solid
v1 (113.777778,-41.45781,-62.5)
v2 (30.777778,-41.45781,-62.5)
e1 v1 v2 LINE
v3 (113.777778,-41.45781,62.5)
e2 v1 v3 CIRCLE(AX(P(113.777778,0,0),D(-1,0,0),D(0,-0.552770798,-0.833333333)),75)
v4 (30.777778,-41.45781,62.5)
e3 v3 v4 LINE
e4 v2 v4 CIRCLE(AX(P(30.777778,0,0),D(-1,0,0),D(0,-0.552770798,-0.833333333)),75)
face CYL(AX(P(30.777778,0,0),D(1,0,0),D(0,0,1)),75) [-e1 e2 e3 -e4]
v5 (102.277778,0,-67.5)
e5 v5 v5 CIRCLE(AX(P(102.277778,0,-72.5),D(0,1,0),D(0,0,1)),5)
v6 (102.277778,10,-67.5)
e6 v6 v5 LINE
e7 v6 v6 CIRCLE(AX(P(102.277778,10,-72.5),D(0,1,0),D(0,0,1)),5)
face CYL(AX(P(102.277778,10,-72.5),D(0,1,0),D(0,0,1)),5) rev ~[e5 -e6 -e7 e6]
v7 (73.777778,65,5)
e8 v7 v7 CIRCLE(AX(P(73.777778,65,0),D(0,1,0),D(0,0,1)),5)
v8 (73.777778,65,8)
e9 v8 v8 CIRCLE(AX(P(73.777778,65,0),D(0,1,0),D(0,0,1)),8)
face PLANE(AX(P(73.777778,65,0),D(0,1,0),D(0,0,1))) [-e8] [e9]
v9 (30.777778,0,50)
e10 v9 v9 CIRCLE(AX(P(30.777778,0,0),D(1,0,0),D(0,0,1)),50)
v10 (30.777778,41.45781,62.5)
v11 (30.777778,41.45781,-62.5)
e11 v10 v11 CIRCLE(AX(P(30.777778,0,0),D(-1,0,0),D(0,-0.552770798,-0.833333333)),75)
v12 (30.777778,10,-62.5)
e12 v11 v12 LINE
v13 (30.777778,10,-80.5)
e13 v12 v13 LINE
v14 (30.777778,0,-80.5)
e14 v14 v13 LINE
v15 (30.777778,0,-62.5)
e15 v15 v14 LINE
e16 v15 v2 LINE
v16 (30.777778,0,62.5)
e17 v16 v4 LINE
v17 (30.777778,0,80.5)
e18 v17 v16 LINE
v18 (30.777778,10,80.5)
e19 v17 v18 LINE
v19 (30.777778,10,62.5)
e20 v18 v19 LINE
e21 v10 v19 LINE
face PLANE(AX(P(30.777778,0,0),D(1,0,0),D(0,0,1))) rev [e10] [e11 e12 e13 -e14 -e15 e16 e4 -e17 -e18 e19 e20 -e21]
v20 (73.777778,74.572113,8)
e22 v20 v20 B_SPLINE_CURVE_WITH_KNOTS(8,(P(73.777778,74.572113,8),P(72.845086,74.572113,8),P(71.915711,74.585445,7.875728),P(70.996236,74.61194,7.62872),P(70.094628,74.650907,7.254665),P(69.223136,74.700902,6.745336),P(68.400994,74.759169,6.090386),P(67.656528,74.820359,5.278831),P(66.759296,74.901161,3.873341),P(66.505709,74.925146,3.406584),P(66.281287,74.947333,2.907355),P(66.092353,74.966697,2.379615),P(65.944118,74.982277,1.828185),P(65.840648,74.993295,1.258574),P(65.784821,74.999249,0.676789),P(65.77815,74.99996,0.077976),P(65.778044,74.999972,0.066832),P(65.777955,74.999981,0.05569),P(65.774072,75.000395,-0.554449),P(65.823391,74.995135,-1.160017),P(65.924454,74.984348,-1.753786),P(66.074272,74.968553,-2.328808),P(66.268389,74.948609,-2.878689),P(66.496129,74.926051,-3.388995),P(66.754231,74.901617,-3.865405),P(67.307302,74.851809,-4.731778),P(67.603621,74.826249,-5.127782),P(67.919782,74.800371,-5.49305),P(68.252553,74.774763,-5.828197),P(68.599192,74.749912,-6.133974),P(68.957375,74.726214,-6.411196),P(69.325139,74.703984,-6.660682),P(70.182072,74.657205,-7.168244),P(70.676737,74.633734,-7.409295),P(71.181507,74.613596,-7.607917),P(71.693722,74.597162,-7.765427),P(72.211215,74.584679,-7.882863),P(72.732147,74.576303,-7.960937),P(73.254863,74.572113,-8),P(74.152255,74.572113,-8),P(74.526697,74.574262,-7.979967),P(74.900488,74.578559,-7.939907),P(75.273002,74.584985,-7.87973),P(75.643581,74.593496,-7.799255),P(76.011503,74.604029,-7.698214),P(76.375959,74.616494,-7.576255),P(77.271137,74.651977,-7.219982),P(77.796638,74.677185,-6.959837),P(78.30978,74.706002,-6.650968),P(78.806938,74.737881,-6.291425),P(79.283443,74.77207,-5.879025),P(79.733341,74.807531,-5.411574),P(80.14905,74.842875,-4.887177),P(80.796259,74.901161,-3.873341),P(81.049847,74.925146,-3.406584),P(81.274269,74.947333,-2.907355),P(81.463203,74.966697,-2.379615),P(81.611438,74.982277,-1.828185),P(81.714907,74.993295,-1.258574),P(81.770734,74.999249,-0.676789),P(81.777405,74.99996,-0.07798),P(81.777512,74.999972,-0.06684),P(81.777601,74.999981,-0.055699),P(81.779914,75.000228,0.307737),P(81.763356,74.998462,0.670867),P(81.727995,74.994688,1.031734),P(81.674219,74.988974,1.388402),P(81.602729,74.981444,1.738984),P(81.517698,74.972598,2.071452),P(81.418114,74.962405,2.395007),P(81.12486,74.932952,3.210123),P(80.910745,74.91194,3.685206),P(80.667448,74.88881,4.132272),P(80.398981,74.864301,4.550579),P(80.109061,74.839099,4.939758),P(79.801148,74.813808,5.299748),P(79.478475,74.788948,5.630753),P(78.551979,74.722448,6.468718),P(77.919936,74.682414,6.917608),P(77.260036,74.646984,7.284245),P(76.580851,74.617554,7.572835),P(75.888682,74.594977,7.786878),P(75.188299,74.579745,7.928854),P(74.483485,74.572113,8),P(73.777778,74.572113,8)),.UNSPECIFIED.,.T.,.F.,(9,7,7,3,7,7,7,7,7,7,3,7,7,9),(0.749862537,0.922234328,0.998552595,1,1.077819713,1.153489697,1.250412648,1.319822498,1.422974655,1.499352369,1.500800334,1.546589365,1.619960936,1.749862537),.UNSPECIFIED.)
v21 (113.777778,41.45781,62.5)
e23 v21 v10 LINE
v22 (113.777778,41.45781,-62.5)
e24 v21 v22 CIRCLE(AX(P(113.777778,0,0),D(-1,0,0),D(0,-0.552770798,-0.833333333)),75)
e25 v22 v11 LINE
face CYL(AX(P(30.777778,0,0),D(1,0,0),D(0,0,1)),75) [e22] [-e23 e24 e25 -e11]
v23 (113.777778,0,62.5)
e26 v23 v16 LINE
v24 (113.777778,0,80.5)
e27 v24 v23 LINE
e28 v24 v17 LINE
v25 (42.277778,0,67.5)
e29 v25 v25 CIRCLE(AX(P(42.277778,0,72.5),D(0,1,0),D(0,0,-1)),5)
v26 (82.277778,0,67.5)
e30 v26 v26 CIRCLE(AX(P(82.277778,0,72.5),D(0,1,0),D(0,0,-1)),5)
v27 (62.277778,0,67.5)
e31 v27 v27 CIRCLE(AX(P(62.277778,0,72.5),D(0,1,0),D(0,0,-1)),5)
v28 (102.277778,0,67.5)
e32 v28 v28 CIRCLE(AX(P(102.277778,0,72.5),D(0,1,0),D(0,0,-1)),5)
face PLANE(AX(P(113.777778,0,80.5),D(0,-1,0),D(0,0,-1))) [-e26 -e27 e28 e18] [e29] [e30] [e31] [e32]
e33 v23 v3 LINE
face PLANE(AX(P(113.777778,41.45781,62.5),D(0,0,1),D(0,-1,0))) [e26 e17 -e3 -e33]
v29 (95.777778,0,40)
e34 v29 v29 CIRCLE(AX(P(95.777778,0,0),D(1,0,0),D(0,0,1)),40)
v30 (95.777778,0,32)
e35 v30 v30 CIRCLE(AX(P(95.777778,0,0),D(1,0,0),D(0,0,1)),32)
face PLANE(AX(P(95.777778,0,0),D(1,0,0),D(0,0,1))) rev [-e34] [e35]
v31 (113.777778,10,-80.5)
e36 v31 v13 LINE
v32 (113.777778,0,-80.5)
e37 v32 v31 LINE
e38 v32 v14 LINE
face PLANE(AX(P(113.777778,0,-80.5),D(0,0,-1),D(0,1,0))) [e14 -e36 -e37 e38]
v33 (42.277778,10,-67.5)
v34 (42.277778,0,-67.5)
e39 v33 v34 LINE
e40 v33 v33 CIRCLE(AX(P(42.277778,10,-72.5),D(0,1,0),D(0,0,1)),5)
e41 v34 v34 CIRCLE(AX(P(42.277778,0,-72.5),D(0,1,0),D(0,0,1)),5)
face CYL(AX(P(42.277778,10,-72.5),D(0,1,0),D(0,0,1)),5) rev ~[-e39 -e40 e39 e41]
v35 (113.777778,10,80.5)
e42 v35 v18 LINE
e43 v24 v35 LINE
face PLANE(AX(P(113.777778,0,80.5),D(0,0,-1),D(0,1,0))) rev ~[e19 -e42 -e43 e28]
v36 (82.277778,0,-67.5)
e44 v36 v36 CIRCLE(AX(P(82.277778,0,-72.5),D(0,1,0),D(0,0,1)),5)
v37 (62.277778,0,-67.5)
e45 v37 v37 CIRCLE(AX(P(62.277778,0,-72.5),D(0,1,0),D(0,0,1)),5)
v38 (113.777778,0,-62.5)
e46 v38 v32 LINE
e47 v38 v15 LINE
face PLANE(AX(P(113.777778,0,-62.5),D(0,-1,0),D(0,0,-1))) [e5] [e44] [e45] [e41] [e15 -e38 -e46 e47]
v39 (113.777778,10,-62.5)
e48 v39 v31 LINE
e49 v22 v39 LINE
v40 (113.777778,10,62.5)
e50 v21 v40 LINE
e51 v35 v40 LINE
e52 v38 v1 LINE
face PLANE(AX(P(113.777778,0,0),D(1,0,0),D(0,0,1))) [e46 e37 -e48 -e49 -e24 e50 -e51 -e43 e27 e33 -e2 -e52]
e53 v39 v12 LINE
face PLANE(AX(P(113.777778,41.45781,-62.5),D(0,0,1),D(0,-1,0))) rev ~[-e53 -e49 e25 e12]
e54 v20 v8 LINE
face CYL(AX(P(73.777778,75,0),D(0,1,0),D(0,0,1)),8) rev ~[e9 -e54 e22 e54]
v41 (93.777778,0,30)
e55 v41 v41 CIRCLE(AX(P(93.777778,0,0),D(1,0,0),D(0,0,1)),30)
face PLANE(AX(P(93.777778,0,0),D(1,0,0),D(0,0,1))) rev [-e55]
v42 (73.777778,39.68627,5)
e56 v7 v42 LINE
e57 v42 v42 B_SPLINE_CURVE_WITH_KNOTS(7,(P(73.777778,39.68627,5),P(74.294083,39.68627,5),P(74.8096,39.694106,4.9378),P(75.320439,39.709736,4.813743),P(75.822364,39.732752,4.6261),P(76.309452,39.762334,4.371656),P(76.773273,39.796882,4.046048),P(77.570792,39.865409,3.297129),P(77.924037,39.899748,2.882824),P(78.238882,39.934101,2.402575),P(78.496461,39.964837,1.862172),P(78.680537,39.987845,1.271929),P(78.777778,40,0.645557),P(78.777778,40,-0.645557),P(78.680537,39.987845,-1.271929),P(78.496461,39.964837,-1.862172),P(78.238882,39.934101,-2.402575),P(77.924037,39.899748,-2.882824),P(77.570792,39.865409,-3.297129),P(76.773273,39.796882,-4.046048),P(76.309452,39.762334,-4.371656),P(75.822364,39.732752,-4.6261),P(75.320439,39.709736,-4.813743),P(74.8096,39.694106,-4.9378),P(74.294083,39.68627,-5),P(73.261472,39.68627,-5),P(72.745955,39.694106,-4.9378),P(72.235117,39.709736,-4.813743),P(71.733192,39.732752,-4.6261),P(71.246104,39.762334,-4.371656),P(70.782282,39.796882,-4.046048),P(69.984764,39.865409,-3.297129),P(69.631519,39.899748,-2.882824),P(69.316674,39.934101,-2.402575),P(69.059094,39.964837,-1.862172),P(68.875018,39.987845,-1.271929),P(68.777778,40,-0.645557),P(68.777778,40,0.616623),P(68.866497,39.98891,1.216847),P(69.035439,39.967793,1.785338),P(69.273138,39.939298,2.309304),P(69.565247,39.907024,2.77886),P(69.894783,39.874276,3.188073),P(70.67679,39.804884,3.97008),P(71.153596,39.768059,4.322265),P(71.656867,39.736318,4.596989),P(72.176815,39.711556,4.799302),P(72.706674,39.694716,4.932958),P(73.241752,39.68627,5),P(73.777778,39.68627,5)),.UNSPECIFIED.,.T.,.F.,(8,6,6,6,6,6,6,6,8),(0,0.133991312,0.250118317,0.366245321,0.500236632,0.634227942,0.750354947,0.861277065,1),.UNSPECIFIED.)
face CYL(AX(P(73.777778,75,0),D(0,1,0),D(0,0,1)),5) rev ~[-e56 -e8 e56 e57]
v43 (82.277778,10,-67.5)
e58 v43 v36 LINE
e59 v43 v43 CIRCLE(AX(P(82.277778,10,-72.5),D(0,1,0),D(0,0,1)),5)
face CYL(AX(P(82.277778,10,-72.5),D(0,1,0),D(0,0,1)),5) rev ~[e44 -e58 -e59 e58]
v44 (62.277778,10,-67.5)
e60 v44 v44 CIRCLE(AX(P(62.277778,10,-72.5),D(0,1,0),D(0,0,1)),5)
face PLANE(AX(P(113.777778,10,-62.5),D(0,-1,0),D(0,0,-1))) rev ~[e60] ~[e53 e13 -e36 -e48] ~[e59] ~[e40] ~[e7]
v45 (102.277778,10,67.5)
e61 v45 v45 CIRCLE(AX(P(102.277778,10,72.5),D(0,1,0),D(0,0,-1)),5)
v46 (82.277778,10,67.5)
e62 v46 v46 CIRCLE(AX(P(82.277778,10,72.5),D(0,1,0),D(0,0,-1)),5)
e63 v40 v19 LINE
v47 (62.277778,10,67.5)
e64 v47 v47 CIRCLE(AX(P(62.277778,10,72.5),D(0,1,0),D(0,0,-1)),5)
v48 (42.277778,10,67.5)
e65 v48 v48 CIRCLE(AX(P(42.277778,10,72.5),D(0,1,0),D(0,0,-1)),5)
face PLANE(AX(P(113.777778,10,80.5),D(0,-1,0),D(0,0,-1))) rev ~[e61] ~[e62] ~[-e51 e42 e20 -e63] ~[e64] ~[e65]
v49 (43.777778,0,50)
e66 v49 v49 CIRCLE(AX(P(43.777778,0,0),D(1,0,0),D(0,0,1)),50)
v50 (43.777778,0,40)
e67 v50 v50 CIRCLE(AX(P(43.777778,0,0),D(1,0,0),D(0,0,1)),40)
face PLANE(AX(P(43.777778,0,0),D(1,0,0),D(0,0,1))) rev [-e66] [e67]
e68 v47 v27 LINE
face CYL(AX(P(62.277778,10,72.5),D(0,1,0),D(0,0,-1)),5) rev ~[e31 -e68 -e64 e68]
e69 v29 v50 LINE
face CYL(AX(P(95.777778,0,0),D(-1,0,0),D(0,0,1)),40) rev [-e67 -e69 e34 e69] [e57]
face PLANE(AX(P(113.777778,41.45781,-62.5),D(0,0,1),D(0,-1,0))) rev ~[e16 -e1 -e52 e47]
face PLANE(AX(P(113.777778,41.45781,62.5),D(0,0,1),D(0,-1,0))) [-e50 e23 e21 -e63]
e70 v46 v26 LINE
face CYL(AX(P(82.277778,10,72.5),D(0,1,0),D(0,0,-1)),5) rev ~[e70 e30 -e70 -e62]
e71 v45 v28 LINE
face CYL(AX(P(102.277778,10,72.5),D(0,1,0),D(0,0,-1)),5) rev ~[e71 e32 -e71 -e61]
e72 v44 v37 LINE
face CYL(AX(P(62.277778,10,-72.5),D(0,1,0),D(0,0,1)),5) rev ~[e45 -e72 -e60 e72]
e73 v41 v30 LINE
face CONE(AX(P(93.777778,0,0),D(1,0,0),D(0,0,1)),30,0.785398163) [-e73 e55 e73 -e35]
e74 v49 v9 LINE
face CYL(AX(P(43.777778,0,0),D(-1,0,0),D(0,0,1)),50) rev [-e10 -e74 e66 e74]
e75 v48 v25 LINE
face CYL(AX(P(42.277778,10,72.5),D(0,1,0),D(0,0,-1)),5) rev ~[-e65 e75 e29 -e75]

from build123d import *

# Parameters (mm, degrees)
CUT_EXTRUDE_1_REACH      = 136.681
SKETCH_9_W               = 18
SKETCH_9_H               = 10
EXTRUDE_1_DEPTH          = 83
CUT_EXTRUDE_4_REACH      = 165.25
SKETCH_10_R              = 5
CUT_EXTRUDE_5_REACH      = 206.757
CUT_EXTRUDE_5_END_RADIUS = 40
SKETCH_11_R              = 5
SKETCH_12_R              = 8
CUT_EXTRUDE_6_DEPTH      = 10


with BuildPart() as part:
    # 草图1 → 旋转1 (revolve)
    with BuildSketch(Plane.XY, mode=Mode.PRIVATE) as revolve_1_sk:
        Polygon((30.777777778, 50), (30.777777778, 75), (113.777777778, 75), (113.777777778, 0), (93.777777778, 0), (93.777777778, 30), (95.777777778, 32), (95.777777778, 40), (43.777777778, 40), (43.777777778, 50), align=None)
    revolve(revolve_1_sk.sketch.rotate(Axis((-130.37037037, 0, 0), (1, 0, 0)), 90), axis=Axis((-130.37037037, 0, 0), (1, 0, 0)))

    # 草图6 → 切除-拉伸1 (cut, up to next)
    with BuildSketch(Plane(origin=(113.777777778, 0, 0), x_dir=(0, 0, -1), z_dir=(1, 0, 0)), mode=Mode.PRIVATE) as cut_extrude_1_sk1:
        with BuildLine():
            Line((62.5, 41.457809879), (62.5, -41.457809879))
            ThreePointArc((62.5, -41.457809879), (75, 0), (62.5, 41.457809879))
        make_face()
    cut_extrude_1_tool1 = extrude(cut_extrude_1_sk1.sketch, amount=-CUT_EXTRUDE_1_REACH, mode=Mode.PRIVATE) & part.part
    # 草图6 → 切除-拉伸1 (cut, up to next)
    with BuildSketch(Plane(origin=(113.777777778, 0, 0), x_dir=(0, 0, -1), z_dir=(1, 0, 0)), mode=Mode.PRIVATE) as cut_extrude_1_sk2:
        with BuildLine():
            Line((-62.5, 41.457809879), (-62.5, -41.457809879))
            ThreePointArc((-62.5, -41.457809879), (-75, 0), (-62.5, 41.457809879))
        make_face()
    cut_extrude_1_tool2 = extrude(cut_extrude_1_sk2.sketch, amount=-CUT_EXTRUDE_1_REACH, mode=Mode.PRIVATE) & part.part
    add(cut_extrude_1_tool1.solids().sort_by_distance((113.777778, 0, -67.537528))[0], mode=Mode.SUBTRACT)
    add(cut_extrude_1_tool2.solids().sort_by_distance((113.777778, 0, 67.537528))[0], mode=Mode.SUBTRACT)

    # 草图9 → 凸台-拉伸1 (add)
    with BuildSketch(Plane(origin=(113.777777778, 0, 0), x_dir=(0, 0, -1), z_dir=(1, 0, 0))):
        with Locations((-71.5, 5)):
            Rectangle(SKETCH_9_W, SKETCH_9_H)
        with Locations((71.5, 5)):
            Rectangle(SKETCH_9_W, SKETCH_9_H)
    extrude(amount=-EXTRUDE_1_DEPTH)

    # 草图10 → 切除-拉伸4 (cut, up to next)
    with BuildSketch(Plane(origin=(0, 10, 0), x_dir=(1, 0, 0), z_dir=(0, 1, 0)), mode=Mode.PRIVATE) as cut_extrude_4_sk1:
        with Locations(Location((42.277777778, 72.5, 0), (0, 0, 270))):
            Circle(SKETCH_10_R)
    cut_extrude_4_tool1 = extrude(cut_extrude_4_sk1.sketch, amount=-CUT_EXTRUDE_4_REACH, mode=Mode.PRIVATE) & part.part
    # 草图10 → 切除-拉伸4 (cut, up to next)
    with BuildSketch(Plane(origin=(0, 10, 0), x_dir=(1, 0, 0), z_dir=(0, 1, 0)), mode=Mode.PRIVATE) as cut_extrude_4_sk2:
        with Locations(Location((62.277777778, 72.5, 0), (0, 0, 270))):
            Circle(SKETCH_10_R)
    cut_extrude_4_tool2 = extrude(cut_extrude_4_sk2.sketch, amount=-CUT_EXTRUDE_4_REACH, mode=Mode.PRIVATE) & part.part
    # 草图10 → 切除-拉伸4 (cut, up to next)
    with BuildSketch(Plane(origin=(0, 10, 0), x_dir=(1, 0, 0), z_dir=(0, 1, 0)), mode=Mode.PRIVATE) as cut_extrude_4_sk3:
        with Locations(Location((82.277777778, 72.5, 0), (0, 0, 270))):
            Circle(SKETCH_10_R)
    cut_extrude_4_tool3 = extrude(cut_extrude_4_sk3.sketch, amount=-CUT_EXTRUDE_4_REACH, mode=Mode.PRIVATE) & part.part
    # 草图10 → 切除-拉伸4 (cut, up to next)
    with BuildSketch(Plane(origin=(0, 10, 0), x_dir=(1, 0, 0), z_dir=(0, 1, 0)), mode=Mode.PRIVATE) as cut_extrude_4_sk4:
        with Locations(Location((102.277777778, 72.5, 0), (0, 0, 270))):
            Circle(SKETCH_10_R)
    cut_extrude_4_tool4 = extrude(cut_extrude_4_sk4.sketch, amount=-CUT_EXTRUDE_4_REACH, mode=Mode.PRIVATE) & part.part
    # 草图10 → 切除-拉伸4 (cut, up to next)
    with BuildSketch(Plane(origin=(0, 10, 0), x_dir=(1, 0, 0), z_dir=(0, 1, 0)), mode=Mode.PRIVATE) as cut_extrude_4_sk5:
        with Locations(Location((102.277777778, -72.5, 0), (0, 0, 90))):
            Circle(SKETCH_10_R)
    cut_extrude_4_tool5 = extrude(cut_extrude_4_sk5.sketch, amount=-CUT_EXTRUDE_4_REACH, mode=Mode.PRIVATE) & part.part
    # 草图10 → 切除-拉伸4 (cut, up to next)
    with BuildSketch(Plane(origin=(0, 10, 0), x_dir=(1, 0, 0), z_dir=(0, 1, 0)), mode=Mode.PRIVATE) as cut_extrude_4_sk6:
        with Locations(Location((82.277777778, -72.5, 0), (0, 0, 90))):
            Circle(SKETCH_10_R)
    cut_extrude_4_tool6 = extrude(cut_extrude_4_sk6.sketch, amount=-CUT_EXTRUDE_4_REACH, mode=Mode.PRIVATE) & part.part
    # 草图10 → 切除-拉伸4 (cut, up to next)
    with BuildSketch(Plane(origin=(0, 10, 0), x_dir=(1, 0, 0), z_dir=(0, 1, 0)), mode=Mode.PRIVATE) as cut_extrude_4_sk7:
        with Locations(Location((62.277777778, -72.5, 0), (0, 0, 90))):
            Circle(SKETCH_10_R)
    cut_extrude_4_tool7 = extrude(cut_extrude_4_sk7.sketch, amount=-CUT_EXTRUDE_4_REACH, mode=Mode.PRIVATE) & part.part
    # 草图10 → 切除-拉伸4 (cut, up to next)
    with BuildSketch(Plane(origin=(0, 10, 0), x_dir=(1, 0, 0), z_dir=(0, 1, 0)), mode=Mode.PRIVATE) as cut_extrude_4_sk8:
        with Locations(Location((42.277777778, -72.5, 0), (0, 0, 90))):
            Circle(SKETCH_10_R)
    cut_extrude_4_tool8 = extrude(cut_extrude_4_sk8.sketch, amount=-CUT_EXTRUDE_4_REACH, mode=Mode.PRIVATE) & part.part
    add(cut_extrude_4_tool1.solids().sort_by_distance((42.277778, 10, -72.5))[0], mode=Mode.SUBTRACT)
    add(cut_extrude_4_tool2.solids().sort_by_distance((62.277778, 10, -72.5))[0], mode=Mode.SUBTRACT)
    add(cut_extrude_4_tool3.solids().sort_by_distance((82.277778, 10, -72.5))[0], mode=Mode.SUBTRACT)
    add(cut_extrude_4_tool4.solids().sort_by_distance((102.277778, 10, -72.5))[0], mode=Mode.SUBTRACT)
    add(cut_extrude_4_tool5.solids().sort_by_distance((102.277778, 10, 72.5))[0], mode=Mode.SUBTRACT)
    add(cut_extrude_4_tool6.solids().sort_by_distance((82.277778, 10, 72.5))[0], mode=Mode.SUBTRACT)
    add(cut_extrude_4_tool7.solids().sort_by_distance((62.277778, 10, 72.5))[0], mode=Mode.SUBTRACT)
    add(cut_extrude_4_tool8.solids().sort_by_distance((42.277778, 10, 72.5))[0], mode=Mode.SUBTRACT)

    # 切除-拉伸5: up to this cylinder (the profile starts outside it)
    cut_extrude_5_end = Plane(origin=(73.777778, 0, 0), z_dir=(-1, 0, 0)) * Cylinder(CUT_EXTRUDE_5_END_RADIUS, 494.514, mode=Mode.PRIVATE)
    # 草图11 → 切除-拉伸5 (cut, up to the surface)
    with BuildSketch(Plane(origin=(0, 75, 0), x_dir=(1, 0, 0), z_dir=(0, 1, 0)), mode=Mode.PRIVATE) as cut_extrude_5_sk1:
        with Locations(Location((73.777777778, 0, 0), (0, 0, 270))):
            Circle(SKETCH_11_R)
    cut_extrude_5_tool1 = extrude(cut_extrude_5_sk1.sketch, amount=-CUT_EXTRUDE_5_REACH, mode=Mode.PRIVATE) - cut_extrude_5_end
    add(cut_extrude_5_tool1.solids().sort_by_distance((73.777778, 75, 0))[0], mode=Mode.SUBTRACT)

    # 草图12 → 切除-拉伸6 (cut)
    with BuildSketch(Plane(origin=(0, 75, 0), x_dir=(1, 0, 0), z_dir=(0, 1, 0))):
        with Locations(Location((73.777777778, 0, 0), (0, 0, 270))):
            Circle(SKETCH_12_R)
    extrude(amount=-CUT_EXTRUDE_6_DEPTH, mode=Mode.SUBTRACT)


solid = part.part
